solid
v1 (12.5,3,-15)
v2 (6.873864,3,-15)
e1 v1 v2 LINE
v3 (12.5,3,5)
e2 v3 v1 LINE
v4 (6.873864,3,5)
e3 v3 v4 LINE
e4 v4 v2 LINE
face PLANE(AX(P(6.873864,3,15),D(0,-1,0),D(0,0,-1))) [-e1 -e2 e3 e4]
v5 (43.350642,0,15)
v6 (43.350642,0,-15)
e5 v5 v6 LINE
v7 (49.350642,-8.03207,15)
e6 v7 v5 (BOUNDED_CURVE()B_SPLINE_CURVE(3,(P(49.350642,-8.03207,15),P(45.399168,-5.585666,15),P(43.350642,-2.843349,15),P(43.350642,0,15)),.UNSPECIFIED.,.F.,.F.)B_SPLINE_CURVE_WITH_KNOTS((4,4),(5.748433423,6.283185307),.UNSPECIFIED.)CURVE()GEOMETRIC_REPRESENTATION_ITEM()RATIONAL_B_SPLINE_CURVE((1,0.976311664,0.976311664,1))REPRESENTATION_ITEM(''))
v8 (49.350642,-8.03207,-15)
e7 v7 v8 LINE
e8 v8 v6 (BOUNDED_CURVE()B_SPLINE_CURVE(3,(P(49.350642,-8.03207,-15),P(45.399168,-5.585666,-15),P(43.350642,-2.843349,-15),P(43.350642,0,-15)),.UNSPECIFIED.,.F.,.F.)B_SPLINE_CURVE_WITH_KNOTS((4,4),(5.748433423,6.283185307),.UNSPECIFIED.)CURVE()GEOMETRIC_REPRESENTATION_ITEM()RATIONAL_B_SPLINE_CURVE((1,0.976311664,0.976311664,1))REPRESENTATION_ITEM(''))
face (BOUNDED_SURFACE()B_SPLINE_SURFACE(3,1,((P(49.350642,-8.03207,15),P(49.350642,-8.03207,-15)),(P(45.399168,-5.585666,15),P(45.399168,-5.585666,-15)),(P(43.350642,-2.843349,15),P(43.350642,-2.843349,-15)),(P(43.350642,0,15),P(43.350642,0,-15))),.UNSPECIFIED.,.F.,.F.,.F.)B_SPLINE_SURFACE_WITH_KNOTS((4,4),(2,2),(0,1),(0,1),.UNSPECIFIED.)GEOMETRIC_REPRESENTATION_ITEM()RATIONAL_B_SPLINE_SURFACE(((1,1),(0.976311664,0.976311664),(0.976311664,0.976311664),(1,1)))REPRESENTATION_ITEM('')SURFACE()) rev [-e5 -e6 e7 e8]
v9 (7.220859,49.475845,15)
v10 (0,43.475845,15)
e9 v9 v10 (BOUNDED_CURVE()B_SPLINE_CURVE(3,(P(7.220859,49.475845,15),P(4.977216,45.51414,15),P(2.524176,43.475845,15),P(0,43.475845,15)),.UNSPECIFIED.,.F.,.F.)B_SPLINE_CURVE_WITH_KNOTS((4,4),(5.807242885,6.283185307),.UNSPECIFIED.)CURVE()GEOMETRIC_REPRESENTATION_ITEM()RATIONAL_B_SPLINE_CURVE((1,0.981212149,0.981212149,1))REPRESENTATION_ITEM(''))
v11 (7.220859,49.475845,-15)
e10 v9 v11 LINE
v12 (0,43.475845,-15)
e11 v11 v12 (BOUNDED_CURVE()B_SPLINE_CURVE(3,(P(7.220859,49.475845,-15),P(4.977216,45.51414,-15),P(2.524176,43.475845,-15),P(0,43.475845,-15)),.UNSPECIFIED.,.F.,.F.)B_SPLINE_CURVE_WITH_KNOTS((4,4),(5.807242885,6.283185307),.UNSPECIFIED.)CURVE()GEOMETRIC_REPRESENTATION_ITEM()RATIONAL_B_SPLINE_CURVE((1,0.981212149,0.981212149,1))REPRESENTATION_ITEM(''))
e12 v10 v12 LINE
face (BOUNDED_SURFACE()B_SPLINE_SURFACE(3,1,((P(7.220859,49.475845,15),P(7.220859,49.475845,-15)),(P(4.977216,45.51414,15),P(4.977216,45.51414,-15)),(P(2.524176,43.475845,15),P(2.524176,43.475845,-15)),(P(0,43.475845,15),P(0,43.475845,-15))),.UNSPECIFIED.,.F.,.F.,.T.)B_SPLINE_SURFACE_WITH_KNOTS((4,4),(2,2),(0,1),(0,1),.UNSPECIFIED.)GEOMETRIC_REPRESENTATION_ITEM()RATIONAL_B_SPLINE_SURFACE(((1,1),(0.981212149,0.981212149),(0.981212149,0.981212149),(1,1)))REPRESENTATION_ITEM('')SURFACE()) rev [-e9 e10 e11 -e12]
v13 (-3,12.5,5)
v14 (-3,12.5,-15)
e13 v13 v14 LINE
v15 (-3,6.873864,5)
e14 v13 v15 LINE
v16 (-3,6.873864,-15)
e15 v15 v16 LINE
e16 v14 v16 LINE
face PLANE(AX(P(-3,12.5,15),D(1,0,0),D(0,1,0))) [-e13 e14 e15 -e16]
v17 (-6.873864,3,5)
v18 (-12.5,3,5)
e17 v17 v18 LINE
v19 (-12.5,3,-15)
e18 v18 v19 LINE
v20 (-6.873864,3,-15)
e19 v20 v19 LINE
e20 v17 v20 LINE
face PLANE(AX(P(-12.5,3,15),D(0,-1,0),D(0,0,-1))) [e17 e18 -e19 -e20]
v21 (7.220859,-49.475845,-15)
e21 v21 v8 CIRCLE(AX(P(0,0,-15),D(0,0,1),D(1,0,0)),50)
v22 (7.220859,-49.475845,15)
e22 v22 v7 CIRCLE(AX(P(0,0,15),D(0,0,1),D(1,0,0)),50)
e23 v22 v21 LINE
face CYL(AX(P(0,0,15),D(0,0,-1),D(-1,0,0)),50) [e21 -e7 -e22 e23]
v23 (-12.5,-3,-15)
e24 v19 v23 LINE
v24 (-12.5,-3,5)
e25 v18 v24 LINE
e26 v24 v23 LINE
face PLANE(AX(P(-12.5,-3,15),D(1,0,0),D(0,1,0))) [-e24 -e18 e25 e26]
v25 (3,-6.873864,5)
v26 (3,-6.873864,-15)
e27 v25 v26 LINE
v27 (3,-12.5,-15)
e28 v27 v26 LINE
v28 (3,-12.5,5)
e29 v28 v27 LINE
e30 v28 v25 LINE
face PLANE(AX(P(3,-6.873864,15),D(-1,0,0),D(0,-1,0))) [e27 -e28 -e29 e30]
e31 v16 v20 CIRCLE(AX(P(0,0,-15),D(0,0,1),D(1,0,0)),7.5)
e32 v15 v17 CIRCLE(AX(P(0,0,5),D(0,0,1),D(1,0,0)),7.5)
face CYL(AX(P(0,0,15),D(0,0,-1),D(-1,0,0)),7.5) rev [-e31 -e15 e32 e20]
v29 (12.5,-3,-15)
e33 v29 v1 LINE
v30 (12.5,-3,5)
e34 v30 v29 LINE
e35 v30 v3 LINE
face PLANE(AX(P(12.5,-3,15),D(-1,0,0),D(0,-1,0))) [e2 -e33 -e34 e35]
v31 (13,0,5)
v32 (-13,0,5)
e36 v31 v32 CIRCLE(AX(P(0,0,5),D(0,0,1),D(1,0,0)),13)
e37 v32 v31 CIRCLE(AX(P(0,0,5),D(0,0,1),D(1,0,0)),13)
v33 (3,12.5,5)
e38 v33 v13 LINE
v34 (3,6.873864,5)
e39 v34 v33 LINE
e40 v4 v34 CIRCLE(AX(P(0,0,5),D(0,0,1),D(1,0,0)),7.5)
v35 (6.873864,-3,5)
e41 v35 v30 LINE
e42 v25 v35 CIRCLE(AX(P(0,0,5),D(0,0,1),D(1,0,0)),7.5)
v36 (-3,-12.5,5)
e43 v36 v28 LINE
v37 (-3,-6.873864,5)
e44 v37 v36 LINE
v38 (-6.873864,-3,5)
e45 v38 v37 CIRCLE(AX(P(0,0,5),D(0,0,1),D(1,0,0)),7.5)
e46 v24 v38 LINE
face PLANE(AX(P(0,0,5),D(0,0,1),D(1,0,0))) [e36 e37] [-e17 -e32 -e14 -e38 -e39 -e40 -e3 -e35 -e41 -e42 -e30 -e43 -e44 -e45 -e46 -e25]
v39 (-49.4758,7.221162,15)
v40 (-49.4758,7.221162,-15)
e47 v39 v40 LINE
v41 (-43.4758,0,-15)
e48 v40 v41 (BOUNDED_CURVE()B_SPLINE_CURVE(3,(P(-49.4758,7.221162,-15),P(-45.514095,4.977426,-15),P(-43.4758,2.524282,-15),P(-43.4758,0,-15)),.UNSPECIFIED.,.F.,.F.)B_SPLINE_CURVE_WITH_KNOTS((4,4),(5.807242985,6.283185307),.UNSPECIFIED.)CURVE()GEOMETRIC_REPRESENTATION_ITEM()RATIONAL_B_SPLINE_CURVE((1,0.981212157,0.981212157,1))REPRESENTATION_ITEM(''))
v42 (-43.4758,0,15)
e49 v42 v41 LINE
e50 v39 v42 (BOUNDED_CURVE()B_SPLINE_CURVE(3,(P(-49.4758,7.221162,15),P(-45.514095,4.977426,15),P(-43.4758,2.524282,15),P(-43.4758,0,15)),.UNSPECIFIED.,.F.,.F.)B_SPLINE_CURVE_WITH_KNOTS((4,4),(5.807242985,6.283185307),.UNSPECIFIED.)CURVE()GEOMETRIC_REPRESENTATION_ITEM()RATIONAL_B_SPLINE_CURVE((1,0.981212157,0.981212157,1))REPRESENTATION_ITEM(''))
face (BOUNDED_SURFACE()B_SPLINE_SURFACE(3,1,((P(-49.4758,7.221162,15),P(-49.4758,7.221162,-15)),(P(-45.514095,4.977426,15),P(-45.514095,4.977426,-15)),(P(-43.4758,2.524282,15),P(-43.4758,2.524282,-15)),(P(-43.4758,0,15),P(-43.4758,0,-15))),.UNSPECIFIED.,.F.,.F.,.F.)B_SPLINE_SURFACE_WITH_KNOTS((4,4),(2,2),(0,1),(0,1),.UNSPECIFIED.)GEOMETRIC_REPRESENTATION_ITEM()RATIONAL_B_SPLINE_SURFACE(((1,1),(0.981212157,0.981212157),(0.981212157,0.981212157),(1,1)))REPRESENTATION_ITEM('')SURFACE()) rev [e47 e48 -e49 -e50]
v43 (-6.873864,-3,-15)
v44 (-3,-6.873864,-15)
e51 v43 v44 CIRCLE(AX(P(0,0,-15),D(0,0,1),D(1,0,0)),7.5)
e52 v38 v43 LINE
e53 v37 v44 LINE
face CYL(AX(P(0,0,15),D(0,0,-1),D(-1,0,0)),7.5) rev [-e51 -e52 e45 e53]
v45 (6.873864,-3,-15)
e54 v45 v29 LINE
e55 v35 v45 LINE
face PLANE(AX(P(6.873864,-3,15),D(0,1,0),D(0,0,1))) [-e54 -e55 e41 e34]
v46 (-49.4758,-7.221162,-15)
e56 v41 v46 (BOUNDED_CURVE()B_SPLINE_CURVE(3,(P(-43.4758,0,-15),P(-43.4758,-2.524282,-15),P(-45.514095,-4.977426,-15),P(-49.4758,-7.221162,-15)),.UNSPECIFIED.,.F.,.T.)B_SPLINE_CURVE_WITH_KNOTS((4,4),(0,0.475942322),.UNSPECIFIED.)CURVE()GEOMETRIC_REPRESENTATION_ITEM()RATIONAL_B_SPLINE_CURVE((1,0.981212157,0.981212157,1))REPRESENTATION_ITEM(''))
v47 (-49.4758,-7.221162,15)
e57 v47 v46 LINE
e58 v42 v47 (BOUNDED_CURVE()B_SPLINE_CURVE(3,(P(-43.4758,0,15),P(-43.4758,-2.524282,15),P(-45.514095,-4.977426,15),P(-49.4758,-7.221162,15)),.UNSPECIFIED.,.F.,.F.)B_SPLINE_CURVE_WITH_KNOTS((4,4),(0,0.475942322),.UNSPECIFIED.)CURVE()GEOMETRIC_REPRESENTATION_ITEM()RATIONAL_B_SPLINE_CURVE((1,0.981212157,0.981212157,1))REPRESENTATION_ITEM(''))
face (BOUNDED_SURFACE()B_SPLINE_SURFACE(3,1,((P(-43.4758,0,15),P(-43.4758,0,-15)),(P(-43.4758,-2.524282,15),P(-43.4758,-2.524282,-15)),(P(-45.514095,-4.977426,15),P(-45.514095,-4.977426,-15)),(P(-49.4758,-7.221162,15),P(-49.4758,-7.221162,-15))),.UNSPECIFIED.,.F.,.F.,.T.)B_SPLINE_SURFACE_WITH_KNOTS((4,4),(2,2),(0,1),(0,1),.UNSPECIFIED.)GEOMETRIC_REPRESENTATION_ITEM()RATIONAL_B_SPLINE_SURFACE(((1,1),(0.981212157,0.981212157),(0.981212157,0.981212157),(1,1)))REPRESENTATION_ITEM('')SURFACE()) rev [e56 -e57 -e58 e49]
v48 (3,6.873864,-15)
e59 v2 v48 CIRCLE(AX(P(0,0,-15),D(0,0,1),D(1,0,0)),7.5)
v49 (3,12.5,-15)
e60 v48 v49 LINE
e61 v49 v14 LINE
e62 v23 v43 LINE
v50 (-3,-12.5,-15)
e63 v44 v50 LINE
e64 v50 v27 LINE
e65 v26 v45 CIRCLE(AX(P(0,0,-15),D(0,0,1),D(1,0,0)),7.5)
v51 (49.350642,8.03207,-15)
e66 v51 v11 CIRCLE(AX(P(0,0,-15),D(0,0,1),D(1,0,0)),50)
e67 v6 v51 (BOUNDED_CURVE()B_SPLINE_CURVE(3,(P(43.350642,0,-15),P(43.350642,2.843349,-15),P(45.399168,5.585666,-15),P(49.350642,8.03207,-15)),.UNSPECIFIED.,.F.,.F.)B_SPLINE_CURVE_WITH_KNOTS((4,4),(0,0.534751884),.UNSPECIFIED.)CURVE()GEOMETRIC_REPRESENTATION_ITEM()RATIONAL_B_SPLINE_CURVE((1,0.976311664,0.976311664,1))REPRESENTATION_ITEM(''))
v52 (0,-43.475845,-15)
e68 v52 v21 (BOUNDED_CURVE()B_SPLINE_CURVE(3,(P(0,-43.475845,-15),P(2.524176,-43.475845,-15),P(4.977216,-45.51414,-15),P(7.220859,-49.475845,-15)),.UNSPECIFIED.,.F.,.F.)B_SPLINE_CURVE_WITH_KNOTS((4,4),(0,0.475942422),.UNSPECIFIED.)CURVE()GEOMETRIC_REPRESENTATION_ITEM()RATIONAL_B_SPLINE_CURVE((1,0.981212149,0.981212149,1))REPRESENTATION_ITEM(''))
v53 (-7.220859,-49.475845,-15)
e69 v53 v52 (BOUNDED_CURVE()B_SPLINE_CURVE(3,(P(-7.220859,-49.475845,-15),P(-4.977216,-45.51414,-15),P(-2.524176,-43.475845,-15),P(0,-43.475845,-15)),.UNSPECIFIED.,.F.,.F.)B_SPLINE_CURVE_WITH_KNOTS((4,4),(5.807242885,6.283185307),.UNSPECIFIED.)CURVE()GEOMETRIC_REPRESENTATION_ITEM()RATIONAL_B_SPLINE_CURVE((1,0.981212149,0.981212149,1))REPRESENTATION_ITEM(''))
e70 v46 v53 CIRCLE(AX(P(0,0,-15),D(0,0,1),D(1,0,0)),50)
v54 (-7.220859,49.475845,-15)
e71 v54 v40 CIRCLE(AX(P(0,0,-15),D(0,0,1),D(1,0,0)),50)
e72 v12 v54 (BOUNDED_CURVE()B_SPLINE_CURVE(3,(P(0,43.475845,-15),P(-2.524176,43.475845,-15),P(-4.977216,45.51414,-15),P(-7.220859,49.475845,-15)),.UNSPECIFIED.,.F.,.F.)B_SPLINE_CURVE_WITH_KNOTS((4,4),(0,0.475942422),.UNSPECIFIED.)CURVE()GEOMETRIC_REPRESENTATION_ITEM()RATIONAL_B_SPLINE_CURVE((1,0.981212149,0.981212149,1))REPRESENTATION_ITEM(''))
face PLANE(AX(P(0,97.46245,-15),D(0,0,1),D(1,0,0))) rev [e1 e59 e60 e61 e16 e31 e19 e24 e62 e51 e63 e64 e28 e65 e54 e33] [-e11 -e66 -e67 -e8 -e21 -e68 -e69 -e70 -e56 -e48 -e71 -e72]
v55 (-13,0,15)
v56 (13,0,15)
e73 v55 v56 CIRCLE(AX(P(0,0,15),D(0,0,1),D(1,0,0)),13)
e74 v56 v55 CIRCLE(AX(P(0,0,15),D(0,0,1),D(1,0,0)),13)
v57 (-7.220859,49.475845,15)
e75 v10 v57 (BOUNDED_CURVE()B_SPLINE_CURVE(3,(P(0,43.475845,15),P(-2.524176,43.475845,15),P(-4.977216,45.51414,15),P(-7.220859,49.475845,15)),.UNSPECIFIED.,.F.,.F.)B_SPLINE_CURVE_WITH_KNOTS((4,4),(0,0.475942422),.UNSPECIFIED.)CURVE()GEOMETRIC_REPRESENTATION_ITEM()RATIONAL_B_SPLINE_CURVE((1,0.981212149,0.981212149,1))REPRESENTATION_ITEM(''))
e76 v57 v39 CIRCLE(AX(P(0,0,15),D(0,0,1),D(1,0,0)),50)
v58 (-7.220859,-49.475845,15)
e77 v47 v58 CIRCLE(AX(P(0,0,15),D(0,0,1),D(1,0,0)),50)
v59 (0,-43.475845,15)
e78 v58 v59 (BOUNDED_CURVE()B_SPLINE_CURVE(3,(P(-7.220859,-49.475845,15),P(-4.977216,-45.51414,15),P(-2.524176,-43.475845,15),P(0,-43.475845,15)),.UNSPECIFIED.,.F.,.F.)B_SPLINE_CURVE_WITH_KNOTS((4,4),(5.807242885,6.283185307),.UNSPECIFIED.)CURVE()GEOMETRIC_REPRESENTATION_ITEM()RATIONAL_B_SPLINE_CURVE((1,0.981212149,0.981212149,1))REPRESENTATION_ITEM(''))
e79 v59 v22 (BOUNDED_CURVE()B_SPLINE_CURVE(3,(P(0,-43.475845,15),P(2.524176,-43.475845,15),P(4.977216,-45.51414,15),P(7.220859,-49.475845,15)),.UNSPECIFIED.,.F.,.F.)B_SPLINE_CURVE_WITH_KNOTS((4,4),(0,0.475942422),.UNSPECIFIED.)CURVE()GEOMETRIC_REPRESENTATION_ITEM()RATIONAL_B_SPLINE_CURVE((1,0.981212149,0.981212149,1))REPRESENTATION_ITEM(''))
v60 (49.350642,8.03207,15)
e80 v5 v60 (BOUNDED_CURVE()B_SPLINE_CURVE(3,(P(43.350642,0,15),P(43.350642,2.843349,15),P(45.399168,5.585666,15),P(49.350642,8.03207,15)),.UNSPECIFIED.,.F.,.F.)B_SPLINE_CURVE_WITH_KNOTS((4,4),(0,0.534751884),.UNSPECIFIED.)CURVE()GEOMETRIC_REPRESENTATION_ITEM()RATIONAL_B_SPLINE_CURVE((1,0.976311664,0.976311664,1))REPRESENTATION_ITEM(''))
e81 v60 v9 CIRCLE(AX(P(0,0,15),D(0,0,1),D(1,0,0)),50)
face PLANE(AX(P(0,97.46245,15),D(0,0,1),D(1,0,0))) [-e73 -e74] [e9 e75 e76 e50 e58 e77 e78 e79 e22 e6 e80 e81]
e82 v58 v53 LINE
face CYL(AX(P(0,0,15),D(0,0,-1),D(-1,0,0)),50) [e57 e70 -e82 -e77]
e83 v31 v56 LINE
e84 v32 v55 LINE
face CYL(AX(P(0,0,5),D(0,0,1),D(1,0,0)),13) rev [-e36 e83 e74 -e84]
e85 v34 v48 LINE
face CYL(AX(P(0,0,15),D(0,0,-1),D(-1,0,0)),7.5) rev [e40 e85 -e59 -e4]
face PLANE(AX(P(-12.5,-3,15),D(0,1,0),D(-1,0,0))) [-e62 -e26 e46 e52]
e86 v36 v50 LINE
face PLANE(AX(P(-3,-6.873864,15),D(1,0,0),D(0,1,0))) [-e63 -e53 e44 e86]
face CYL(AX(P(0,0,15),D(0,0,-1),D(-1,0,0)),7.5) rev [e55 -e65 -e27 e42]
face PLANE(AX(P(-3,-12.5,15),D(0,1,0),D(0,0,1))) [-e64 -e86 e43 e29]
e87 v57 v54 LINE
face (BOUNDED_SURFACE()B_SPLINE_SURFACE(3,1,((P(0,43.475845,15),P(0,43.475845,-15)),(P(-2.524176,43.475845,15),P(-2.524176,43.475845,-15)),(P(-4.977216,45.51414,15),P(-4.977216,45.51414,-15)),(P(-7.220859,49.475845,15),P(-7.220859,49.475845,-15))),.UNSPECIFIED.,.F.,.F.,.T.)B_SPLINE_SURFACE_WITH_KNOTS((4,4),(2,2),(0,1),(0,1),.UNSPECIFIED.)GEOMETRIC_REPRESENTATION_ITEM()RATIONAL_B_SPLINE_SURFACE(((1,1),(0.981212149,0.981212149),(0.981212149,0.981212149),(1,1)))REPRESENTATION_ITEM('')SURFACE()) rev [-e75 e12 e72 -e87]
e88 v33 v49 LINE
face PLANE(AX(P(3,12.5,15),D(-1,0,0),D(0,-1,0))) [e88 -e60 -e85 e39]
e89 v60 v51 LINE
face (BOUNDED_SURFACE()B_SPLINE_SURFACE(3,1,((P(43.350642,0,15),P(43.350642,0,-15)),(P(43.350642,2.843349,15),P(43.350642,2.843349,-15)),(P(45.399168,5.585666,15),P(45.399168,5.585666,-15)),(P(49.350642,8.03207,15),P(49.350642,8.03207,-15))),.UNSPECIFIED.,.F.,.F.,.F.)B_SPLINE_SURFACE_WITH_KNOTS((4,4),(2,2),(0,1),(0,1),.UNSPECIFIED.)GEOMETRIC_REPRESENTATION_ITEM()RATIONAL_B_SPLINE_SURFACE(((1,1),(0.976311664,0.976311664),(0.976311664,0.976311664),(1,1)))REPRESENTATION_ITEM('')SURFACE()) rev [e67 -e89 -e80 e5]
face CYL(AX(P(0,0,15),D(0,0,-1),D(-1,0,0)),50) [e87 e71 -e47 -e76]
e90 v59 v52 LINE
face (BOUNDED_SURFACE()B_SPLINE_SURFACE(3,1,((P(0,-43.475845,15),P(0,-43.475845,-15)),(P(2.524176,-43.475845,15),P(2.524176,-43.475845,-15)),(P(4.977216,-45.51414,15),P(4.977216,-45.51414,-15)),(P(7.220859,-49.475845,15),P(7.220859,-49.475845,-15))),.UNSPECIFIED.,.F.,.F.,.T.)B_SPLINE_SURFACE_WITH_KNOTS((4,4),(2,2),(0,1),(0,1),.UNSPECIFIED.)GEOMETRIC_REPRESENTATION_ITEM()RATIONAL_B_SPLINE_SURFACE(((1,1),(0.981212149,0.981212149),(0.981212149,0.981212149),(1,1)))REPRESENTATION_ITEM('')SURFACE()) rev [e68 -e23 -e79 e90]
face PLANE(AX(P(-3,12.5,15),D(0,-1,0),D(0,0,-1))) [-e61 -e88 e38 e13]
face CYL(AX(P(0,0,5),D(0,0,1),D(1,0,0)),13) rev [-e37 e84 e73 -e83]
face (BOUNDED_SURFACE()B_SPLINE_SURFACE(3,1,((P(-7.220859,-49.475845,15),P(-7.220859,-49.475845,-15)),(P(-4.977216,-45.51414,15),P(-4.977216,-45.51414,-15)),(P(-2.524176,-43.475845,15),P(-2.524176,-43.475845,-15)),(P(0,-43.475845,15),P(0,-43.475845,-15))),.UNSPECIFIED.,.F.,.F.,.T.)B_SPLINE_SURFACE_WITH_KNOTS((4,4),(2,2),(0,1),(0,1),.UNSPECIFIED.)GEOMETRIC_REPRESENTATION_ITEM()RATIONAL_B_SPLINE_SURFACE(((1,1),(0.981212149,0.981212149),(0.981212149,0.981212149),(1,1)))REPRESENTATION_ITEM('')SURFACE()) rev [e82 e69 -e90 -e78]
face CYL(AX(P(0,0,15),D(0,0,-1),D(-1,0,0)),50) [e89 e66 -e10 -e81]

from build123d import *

# Parameters (mm, degrees)
EXTRUDE_1_DEPTH     = 15
SKETCH_2_R          = 13
CUT_EXTRUDE_2_DEPTH = 10


with BuildPart() as part:
    # 草图1 → 拉伸1 (new, symmetric)
    with BuildSketch(Plane.XY):
        with BuildLine():
            ThreePointArc((-7.220859013, 49.475844562), (-35.355230678, 35.355447441), (-49.47580029, 7.221162349))
            add(Edge.make_bspline(
                [(-49.47580029, -7.221162349), (-36.725591286, 0), (-49.47580029, 7.221162349)],
                knots=[2.665650331, 2.665650331, 2.665650331, 3.617534976, 3.617534976, 3.617534976], degree=2, weights=[1, 0.888861367, 1]))
            ThreePointArc((-49.47580029, -7.221162349), (-35.355230678, -35.355447441), (-7.220859013, -49.475844562))
            add(Edge.make_bspline(
                [(7.220859013, -49.475844562), (0, -36.72563521), (-7.220859013, -49.475844562)],
                knots=[2.665650231, 2.665650231, 2.665650231, 3.617535076, 3.617535076, 3.617535076], degree=2, weights=[1, 0.888861321, 1]))
            ThreePointArc((7.220859013, -49.475844562), (35.063945901, -35.644350154), (49.350641932, -8.032069525))
            add(Edge.make_bspline(
                [(49.350641932, 8.032069525), (36.37710154, 0), (49.350641932, -8.032069525)],
                knots=[5.748433423, 5.748433423, 5.748433423, 6.817937192, 6.817937192, 6.817937192], degree=2, weights=[1, 0.860395102, 1]))
            ThreePointArc((49.350641932, 8.032069525), (35.063945901, 35.644350154), (7.220859013, 49.475844562))
            add(Edge.make_bspline(
                [(-7.220859013, 49.475844562), (0, 36.72563521), (7.220859013, 49.475844562)],
                knots=[2.665650231, 2.665650231, 2.665650231, 3.617535076, 3.617535076, 3.617535076], degree=2, weights=[1, 0.888861321, 1]))
        make_face()
        with BuildLine():
            Line((3, -6.873863542), (3, -12.5))
            Line((3, -12.5), (-3, -12.5))
            Line((-3, -12.5), (-3, -6.873863542))
            ThreePointArc((-3, -6.873863542), (-5.303300859, -5.303300859), (-6.873863542, -3))
            Line((-6.873863542, -3), (-12.5, -3))
            Line((-12.5, -3), (-12.5, 3))
            Line((-12.5, 3), (-6.873863542, 3))
            ThreePointArc((-6.873863542, 3), (-5.303300859, 5.303300859), (-3, 6.873863542))
            Line((-3, 6.873863542), (-3, 12.5))
            Line((-3, 12.5), (3, 12.5))
            Line((3, 12.5), (3, 6.873863542))
            ThreePointArc((3, 6.873863542), (5.303300859, 5.303300859), (6.873863542, 3))
            Line((6.873863542, 3), (12.5, 3))
            Line((12.5, 3), (12.5, -3))
            Line((12.5, -3), (6.873863542, -3))
            ThreePointArc((6.873863542, -3), (5.303300859, -5.303300859), (3, -6.873863542))
        make_face(mode=Mode.SUBTRACT)
    extrude(amount=EXTRUDE_1_DEPTH, both=True)

    # 草图2 → 拉伸2 (cut)
    with BuildSketch(Plane.XY.offset(15)):
        Circle(SKETCH_2_R)
    extrude(amount=-CUT_EXTRUDE_2_DEPTH, mode=Mode.SUBTRACT)


solid = part.part
